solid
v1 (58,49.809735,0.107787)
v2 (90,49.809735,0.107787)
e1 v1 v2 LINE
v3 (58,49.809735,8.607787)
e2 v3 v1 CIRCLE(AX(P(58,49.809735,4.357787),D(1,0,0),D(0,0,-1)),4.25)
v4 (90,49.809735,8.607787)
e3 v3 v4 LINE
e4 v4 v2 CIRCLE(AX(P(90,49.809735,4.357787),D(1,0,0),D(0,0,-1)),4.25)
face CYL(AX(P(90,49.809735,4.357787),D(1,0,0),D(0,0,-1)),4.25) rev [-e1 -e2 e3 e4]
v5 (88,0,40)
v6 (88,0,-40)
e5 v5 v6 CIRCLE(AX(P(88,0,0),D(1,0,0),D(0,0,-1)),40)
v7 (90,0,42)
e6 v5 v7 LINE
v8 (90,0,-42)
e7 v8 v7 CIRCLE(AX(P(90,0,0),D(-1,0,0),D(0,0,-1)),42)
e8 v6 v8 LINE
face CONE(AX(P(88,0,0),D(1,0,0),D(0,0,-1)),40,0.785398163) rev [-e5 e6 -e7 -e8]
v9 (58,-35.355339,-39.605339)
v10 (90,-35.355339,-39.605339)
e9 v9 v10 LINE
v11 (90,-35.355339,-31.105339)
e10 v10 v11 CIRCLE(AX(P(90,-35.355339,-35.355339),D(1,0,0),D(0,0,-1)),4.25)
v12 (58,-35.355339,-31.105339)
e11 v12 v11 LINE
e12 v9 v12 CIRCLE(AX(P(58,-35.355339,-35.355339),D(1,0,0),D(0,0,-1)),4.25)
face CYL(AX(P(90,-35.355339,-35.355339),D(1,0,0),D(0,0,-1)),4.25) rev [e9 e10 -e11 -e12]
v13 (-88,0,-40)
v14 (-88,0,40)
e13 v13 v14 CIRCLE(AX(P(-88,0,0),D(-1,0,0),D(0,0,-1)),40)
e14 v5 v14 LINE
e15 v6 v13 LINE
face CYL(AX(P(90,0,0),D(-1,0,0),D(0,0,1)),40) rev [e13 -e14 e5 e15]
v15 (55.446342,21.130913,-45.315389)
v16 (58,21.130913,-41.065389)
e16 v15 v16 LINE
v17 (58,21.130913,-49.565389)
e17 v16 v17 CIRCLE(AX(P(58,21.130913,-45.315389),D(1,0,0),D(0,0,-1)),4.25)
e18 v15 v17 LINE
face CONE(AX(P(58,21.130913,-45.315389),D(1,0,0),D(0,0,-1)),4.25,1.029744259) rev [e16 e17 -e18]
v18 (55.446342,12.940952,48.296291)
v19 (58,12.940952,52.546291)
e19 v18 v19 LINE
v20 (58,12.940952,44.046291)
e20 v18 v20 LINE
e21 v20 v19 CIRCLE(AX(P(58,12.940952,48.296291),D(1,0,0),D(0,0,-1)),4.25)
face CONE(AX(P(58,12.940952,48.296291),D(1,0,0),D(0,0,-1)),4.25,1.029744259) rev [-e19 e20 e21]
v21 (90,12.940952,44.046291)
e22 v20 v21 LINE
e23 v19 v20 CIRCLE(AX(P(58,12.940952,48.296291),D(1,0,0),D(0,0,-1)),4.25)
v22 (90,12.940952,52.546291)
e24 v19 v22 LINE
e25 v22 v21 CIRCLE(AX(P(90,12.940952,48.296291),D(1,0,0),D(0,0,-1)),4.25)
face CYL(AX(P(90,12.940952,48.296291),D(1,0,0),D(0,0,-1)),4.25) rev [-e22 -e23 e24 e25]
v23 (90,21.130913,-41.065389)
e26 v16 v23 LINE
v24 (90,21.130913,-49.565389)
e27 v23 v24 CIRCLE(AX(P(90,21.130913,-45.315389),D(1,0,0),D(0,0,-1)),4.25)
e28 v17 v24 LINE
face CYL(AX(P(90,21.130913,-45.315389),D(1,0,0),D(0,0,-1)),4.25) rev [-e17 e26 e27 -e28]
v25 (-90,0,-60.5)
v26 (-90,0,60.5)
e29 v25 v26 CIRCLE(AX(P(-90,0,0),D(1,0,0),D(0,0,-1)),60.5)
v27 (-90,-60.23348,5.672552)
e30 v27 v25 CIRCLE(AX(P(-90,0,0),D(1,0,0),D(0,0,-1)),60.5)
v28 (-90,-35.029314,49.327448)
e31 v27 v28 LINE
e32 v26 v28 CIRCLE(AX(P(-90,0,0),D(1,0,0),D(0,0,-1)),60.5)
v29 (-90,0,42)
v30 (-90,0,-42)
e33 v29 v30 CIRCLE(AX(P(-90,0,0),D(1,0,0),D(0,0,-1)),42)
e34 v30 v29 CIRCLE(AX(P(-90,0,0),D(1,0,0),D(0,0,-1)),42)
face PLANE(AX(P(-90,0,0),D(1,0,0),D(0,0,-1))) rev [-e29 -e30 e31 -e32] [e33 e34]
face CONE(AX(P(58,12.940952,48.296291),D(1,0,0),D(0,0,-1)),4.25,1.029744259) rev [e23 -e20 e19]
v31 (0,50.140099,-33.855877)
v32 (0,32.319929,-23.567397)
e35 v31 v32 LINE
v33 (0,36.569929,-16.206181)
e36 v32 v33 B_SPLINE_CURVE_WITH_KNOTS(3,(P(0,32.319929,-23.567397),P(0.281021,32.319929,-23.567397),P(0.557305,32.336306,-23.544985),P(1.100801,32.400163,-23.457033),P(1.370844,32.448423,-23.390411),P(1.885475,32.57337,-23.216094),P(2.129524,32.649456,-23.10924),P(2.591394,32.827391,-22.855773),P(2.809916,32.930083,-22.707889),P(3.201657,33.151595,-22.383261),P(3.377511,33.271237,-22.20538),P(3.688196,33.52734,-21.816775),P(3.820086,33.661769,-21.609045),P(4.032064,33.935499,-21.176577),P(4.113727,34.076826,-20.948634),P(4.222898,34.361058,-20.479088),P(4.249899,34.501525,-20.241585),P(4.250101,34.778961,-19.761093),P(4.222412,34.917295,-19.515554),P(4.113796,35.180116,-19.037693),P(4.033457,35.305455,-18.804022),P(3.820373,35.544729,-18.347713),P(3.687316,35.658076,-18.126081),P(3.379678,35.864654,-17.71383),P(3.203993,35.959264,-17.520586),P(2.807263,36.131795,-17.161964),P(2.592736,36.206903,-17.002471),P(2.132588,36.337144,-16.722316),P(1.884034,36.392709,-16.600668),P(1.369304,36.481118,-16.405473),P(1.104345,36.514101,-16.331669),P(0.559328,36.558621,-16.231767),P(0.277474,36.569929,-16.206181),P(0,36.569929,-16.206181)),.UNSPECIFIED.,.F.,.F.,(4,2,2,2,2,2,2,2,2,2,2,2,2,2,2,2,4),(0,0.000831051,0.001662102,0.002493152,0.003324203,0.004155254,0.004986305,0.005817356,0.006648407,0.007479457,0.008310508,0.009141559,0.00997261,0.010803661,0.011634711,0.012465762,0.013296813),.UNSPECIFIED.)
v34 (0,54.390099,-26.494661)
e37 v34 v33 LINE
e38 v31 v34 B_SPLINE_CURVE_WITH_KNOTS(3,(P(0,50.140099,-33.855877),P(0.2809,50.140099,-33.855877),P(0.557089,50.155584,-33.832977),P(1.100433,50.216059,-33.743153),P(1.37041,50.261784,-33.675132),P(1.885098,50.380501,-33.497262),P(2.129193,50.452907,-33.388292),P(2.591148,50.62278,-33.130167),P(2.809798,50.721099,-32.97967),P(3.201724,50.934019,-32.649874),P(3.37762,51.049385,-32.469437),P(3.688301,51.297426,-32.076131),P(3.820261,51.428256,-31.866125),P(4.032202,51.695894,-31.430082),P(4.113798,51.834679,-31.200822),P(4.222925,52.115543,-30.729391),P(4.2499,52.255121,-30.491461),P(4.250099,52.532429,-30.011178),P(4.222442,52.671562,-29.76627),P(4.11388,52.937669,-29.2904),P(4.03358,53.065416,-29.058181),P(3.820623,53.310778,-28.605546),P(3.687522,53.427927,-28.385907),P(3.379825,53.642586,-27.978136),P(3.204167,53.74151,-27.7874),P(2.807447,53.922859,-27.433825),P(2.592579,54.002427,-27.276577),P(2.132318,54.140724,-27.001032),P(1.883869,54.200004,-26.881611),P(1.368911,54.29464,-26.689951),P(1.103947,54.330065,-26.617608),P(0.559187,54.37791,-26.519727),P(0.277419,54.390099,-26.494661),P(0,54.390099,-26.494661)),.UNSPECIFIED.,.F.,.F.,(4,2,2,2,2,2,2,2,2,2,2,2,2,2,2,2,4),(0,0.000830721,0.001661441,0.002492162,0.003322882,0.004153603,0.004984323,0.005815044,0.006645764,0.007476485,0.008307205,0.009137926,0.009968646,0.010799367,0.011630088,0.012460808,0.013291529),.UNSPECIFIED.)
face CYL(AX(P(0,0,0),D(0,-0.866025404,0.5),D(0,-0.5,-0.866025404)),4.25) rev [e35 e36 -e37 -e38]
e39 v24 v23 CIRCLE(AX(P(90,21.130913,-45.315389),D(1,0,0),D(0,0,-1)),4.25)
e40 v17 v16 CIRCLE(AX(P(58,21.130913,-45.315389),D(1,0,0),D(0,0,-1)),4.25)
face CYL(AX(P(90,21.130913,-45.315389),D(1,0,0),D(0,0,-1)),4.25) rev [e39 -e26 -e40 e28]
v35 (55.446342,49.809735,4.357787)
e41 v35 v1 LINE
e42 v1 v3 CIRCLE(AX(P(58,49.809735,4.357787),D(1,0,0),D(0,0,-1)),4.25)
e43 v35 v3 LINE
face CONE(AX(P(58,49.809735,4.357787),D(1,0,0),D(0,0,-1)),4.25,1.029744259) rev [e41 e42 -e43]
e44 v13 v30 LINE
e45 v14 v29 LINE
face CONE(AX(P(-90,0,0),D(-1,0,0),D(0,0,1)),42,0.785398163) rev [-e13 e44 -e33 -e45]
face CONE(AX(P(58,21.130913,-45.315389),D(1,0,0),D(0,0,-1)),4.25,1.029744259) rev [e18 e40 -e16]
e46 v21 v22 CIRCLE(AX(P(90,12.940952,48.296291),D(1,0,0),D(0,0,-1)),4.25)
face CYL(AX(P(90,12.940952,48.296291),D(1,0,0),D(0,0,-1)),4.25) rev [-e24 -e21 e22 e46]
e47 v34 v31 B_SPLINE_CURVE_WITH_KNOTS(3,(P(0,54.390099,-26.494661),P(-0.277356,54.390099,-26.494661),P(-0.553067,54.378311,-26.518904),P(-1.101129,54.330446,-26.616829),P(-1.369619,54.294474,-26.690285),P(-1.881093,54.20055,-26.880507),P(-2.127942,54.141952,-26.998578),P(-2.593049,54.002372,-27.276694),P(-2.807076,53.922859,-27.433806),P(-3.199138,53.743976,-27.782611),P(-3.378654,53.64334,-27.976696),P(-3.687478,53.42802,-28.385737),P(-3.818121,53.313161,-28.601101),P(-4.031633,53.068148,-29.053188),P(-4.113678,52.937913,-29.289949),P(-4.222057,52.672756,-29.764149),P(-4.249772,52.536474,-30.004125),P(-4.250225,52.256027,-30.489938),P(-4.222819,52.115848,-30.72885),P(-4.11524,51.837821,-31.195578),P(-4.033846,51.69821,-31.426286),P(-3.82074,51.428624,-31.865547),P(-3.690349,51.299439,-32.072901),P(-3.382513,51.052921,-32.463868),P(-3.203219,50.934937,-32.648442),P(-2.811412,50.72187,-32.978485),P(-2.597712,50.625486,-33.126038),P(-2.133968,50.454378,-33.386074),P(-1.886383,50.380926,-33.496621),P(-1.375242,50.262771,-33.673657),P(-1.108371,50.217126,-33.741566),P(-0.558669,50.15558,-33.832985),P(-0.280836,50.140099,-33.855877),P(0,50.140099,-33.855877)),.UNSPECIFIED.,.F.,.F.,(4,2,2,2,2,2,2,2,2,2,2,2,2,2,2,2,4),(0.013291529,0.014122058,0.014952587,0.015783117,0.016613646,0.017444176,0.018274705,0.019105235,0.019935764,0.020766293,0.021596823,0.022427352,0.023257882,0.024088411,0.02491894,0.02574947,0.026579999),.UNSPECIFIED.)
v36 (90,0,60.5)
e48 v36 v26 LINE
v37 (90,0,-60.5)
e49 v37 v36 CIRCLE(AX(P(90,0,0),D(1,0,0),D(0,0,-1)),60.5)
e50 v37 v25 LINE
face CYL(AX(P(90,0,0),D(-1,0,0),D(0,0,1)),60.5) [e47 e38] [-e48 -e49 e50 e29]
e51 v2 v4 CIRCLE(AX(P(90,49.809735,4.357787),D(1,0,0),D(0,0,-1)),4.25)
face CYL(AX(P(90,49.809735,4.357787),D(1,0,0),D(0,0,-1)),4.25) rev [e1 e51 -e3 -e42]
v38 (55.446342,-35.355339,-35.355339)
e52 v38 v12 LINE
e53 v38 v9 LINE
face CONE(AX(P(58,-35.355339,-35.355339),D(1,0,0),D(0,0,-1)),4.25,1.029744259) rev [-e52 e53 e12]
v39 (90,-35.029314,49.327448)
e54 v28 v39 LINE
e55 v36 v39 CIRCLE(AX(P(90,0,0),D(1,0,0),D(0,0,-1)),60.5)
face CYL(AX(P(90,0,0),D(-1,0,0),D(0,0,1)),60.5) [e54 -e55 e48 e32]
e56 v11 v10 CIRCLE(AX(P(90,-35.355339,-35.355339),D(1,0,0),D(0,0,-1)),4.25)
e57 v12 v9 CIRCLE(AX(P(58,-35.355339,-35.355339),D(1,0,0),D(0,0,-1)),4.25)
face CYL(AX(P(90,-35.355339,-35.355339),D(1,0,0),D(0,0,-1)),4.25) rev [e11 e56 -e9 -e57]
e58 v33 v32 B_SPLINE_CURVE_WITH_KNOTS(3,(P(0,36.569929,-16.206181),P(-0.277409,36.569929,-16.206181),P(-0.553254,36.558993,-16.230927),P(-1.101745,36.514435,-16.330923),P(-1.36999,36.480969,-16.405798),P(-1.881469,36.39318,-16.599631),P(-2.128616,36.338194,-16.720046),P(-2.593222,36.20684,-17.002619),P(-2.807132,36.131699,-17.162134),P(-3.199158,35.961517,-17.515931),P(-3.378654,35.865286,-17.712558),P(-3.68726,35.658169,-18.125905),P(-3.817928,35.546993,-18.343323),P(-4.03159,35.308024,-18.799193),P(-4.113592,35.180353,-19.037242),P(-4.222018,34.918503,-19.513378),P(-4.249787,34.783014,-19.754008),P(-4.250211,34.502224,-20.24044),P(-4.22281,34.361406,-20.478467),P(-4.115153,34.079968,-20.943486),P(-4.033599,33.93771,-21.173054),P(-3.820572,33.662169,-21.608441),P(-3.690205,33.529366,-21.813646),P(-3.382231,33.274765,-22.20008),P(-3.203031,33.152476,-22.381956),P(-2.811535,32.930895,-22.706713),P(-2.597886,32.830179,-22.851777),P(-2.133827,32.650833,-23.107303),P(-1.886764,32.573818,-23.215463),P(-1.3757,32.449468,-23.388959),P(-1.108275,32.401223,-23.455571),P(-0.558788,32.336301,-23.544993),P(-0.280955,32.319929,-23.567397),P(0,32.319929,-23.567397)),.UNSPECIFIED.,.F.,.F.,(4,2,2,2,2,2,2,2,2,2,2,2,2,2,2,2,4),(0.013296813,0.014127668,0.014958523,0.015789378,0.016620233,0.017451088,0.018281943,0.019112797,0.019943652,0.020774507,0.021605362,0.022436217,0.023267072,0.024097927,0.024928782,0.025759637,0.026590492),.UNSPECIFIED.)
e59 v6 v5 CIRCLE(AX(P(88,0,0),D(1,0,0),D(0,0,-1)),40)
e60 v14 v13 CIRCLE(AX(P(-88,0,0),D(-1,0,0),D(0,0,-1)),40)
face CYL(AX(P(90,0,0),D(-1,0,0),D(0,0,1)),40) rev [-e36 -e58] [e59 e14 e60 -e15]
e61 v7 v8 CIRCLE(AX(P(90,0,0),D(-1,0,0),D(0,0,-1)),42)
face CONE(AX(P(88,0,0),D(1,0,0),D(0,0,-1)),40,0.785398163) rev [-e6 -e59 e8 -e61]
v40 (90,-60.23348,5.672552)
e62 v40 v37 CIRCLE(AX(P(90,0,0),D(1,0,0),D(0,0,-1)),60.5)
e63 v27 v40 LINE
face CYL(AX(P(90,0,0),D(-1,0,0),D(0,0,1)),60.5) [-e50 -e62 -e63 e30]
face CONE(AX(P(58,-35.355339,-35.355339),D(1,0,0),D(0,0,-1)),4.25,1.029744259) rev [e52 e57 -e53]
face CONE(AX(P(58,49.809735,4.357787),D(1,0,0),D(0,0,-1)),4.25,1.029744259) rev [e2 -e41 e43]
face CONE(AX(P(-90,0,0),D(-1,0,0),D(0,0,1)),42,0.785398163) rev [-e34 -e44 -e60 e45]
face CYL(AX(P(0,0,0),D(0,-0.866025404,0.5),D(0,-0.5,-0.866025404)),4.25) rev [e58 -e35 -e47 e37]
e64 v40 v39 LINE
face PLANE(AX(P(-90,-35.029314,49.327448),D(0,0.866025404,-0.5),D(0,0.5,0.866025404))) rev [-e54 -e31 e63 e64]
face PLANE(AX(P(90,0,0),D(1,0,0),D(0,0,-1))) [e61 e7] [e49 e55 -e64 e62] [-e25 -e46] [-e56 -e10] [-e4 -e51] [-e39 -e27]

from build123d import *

# Parameters (mm, degrees)
SKETCH1_R               = 60.5
SKETCH1_R_2             = 40
BOSS_EXTRUDE1_DEPTH     = 90
CUT_EXTRUDE1_DEPTH      = 125.179305844
CUT_EXTRUDE1_DEPTH_BACK = 125.179305844
SKETCH6_W               = 4.25
SKETCH6_H               = 82.644536929
M10_TAPPED_HOLE2_D      = 8.5
M10_TAPPED_HOLE2_DEPTH  = 32
M10_TAPPED_HOLE2_TIP    = 2.553657631
CHAMFER1_SIZE           = 2


with BuildPart() as part:
    # Sketch1 → Boss-Extrude1 (new, symmetric)
    with BuildSketch(Plane(origin=(0, 0, 0), x_dir=(0, 0, -1), z_dir=(1, 0, 0))):
        with Locations(Location((0, 0, 0), (0, 0, 180))):
            Circle(SKETCH1_R)
        with Locations(Location((0, 0, 0), (0, 0, 180))):
            Circle(SKETCH1_R_2, mode=Mode.SUBTRACT)
    extrude(amount=BOSS_EXTRUDE1_DEPTH, both=True)

    # Sketch5 → Cut-Extrude1 (cut, two sides: drawn at the far end of the back side and taken through both)
    with BuildSketch(Plane(origin=(0, 0, 0), x_dir=(0, 0, -1), z_dir=(1, 0, 0)).offset(-CUT_EXTRUDE1_DEPTH_BACK)):
        with BuildLine():
            Line((-49.327448316, -35.029314047), (-5.672551684, -60.233480369))
            ThreePointArc((-5.672551684, -60.233480369), (-30.25, -52.394536929), (-49.327448316, -35.029314047))
        make_face()
    extrude(amount=CUT_EXTRUDE1_DEPTH + CUT_EXTRUDE1_DEPTH_BACK, mode=Mode.SUBTRACT)

    # Sketch6 → M10 Tapped Hole1 (revolve, cut)
    with BuildSketch(Plane(origin=(0, 0, 0), x_dir=(0, -0.500000000000001, -0.8660254037844382), z_dir=(1, 0, 0))):
        with Locations((2.125, 41.322268465)):
            Rectangle(SKETCH6_W, SKETCH6_H)
    revolve(axis=Axis((0, -5.499261314, 3.175), (0, 0.866025403784438, -0.500000000000001)), mode=Mode.SUBTRACT)

    # M10 Tapped Hole2
    with Locations(Plane(origin=(90, 0, 0), x_dir=(0, 0, -1), z_dir=(1, 0, 0))):
        with Locations((-4.357787137, 49.809734905), (45.315389352, 21.130913087), (35.355339059, -35.355339059), (-48.296291314, 12.940952255)):
            Hole(M10_TAPPED_HOLE2_D / 2, depth=M10_TAPPED_HOLE2_DEPTH)
            with Locations((0, 0, -(M10_TAPPED_HOLE2_DEPTH + M10_TAPPED_HOLE2_TIP / 2))):  # 118° drill point
                Cone(0, M10_TAPPED_HOLE2_D / 2, M10_TAPPED_HOLE2_TIP, mode=Mode.SUBTRACT)

    # Chamfer1
    chamfer1_edges = [part.edges().sort_by_distance(p)[0] for p in [
        (-90, 0, -40),
        (90, 0, -40),
    ]]
    chamfer(chamfer1_edges, length=CHAMFER1_SIZE)


solid = part.part
